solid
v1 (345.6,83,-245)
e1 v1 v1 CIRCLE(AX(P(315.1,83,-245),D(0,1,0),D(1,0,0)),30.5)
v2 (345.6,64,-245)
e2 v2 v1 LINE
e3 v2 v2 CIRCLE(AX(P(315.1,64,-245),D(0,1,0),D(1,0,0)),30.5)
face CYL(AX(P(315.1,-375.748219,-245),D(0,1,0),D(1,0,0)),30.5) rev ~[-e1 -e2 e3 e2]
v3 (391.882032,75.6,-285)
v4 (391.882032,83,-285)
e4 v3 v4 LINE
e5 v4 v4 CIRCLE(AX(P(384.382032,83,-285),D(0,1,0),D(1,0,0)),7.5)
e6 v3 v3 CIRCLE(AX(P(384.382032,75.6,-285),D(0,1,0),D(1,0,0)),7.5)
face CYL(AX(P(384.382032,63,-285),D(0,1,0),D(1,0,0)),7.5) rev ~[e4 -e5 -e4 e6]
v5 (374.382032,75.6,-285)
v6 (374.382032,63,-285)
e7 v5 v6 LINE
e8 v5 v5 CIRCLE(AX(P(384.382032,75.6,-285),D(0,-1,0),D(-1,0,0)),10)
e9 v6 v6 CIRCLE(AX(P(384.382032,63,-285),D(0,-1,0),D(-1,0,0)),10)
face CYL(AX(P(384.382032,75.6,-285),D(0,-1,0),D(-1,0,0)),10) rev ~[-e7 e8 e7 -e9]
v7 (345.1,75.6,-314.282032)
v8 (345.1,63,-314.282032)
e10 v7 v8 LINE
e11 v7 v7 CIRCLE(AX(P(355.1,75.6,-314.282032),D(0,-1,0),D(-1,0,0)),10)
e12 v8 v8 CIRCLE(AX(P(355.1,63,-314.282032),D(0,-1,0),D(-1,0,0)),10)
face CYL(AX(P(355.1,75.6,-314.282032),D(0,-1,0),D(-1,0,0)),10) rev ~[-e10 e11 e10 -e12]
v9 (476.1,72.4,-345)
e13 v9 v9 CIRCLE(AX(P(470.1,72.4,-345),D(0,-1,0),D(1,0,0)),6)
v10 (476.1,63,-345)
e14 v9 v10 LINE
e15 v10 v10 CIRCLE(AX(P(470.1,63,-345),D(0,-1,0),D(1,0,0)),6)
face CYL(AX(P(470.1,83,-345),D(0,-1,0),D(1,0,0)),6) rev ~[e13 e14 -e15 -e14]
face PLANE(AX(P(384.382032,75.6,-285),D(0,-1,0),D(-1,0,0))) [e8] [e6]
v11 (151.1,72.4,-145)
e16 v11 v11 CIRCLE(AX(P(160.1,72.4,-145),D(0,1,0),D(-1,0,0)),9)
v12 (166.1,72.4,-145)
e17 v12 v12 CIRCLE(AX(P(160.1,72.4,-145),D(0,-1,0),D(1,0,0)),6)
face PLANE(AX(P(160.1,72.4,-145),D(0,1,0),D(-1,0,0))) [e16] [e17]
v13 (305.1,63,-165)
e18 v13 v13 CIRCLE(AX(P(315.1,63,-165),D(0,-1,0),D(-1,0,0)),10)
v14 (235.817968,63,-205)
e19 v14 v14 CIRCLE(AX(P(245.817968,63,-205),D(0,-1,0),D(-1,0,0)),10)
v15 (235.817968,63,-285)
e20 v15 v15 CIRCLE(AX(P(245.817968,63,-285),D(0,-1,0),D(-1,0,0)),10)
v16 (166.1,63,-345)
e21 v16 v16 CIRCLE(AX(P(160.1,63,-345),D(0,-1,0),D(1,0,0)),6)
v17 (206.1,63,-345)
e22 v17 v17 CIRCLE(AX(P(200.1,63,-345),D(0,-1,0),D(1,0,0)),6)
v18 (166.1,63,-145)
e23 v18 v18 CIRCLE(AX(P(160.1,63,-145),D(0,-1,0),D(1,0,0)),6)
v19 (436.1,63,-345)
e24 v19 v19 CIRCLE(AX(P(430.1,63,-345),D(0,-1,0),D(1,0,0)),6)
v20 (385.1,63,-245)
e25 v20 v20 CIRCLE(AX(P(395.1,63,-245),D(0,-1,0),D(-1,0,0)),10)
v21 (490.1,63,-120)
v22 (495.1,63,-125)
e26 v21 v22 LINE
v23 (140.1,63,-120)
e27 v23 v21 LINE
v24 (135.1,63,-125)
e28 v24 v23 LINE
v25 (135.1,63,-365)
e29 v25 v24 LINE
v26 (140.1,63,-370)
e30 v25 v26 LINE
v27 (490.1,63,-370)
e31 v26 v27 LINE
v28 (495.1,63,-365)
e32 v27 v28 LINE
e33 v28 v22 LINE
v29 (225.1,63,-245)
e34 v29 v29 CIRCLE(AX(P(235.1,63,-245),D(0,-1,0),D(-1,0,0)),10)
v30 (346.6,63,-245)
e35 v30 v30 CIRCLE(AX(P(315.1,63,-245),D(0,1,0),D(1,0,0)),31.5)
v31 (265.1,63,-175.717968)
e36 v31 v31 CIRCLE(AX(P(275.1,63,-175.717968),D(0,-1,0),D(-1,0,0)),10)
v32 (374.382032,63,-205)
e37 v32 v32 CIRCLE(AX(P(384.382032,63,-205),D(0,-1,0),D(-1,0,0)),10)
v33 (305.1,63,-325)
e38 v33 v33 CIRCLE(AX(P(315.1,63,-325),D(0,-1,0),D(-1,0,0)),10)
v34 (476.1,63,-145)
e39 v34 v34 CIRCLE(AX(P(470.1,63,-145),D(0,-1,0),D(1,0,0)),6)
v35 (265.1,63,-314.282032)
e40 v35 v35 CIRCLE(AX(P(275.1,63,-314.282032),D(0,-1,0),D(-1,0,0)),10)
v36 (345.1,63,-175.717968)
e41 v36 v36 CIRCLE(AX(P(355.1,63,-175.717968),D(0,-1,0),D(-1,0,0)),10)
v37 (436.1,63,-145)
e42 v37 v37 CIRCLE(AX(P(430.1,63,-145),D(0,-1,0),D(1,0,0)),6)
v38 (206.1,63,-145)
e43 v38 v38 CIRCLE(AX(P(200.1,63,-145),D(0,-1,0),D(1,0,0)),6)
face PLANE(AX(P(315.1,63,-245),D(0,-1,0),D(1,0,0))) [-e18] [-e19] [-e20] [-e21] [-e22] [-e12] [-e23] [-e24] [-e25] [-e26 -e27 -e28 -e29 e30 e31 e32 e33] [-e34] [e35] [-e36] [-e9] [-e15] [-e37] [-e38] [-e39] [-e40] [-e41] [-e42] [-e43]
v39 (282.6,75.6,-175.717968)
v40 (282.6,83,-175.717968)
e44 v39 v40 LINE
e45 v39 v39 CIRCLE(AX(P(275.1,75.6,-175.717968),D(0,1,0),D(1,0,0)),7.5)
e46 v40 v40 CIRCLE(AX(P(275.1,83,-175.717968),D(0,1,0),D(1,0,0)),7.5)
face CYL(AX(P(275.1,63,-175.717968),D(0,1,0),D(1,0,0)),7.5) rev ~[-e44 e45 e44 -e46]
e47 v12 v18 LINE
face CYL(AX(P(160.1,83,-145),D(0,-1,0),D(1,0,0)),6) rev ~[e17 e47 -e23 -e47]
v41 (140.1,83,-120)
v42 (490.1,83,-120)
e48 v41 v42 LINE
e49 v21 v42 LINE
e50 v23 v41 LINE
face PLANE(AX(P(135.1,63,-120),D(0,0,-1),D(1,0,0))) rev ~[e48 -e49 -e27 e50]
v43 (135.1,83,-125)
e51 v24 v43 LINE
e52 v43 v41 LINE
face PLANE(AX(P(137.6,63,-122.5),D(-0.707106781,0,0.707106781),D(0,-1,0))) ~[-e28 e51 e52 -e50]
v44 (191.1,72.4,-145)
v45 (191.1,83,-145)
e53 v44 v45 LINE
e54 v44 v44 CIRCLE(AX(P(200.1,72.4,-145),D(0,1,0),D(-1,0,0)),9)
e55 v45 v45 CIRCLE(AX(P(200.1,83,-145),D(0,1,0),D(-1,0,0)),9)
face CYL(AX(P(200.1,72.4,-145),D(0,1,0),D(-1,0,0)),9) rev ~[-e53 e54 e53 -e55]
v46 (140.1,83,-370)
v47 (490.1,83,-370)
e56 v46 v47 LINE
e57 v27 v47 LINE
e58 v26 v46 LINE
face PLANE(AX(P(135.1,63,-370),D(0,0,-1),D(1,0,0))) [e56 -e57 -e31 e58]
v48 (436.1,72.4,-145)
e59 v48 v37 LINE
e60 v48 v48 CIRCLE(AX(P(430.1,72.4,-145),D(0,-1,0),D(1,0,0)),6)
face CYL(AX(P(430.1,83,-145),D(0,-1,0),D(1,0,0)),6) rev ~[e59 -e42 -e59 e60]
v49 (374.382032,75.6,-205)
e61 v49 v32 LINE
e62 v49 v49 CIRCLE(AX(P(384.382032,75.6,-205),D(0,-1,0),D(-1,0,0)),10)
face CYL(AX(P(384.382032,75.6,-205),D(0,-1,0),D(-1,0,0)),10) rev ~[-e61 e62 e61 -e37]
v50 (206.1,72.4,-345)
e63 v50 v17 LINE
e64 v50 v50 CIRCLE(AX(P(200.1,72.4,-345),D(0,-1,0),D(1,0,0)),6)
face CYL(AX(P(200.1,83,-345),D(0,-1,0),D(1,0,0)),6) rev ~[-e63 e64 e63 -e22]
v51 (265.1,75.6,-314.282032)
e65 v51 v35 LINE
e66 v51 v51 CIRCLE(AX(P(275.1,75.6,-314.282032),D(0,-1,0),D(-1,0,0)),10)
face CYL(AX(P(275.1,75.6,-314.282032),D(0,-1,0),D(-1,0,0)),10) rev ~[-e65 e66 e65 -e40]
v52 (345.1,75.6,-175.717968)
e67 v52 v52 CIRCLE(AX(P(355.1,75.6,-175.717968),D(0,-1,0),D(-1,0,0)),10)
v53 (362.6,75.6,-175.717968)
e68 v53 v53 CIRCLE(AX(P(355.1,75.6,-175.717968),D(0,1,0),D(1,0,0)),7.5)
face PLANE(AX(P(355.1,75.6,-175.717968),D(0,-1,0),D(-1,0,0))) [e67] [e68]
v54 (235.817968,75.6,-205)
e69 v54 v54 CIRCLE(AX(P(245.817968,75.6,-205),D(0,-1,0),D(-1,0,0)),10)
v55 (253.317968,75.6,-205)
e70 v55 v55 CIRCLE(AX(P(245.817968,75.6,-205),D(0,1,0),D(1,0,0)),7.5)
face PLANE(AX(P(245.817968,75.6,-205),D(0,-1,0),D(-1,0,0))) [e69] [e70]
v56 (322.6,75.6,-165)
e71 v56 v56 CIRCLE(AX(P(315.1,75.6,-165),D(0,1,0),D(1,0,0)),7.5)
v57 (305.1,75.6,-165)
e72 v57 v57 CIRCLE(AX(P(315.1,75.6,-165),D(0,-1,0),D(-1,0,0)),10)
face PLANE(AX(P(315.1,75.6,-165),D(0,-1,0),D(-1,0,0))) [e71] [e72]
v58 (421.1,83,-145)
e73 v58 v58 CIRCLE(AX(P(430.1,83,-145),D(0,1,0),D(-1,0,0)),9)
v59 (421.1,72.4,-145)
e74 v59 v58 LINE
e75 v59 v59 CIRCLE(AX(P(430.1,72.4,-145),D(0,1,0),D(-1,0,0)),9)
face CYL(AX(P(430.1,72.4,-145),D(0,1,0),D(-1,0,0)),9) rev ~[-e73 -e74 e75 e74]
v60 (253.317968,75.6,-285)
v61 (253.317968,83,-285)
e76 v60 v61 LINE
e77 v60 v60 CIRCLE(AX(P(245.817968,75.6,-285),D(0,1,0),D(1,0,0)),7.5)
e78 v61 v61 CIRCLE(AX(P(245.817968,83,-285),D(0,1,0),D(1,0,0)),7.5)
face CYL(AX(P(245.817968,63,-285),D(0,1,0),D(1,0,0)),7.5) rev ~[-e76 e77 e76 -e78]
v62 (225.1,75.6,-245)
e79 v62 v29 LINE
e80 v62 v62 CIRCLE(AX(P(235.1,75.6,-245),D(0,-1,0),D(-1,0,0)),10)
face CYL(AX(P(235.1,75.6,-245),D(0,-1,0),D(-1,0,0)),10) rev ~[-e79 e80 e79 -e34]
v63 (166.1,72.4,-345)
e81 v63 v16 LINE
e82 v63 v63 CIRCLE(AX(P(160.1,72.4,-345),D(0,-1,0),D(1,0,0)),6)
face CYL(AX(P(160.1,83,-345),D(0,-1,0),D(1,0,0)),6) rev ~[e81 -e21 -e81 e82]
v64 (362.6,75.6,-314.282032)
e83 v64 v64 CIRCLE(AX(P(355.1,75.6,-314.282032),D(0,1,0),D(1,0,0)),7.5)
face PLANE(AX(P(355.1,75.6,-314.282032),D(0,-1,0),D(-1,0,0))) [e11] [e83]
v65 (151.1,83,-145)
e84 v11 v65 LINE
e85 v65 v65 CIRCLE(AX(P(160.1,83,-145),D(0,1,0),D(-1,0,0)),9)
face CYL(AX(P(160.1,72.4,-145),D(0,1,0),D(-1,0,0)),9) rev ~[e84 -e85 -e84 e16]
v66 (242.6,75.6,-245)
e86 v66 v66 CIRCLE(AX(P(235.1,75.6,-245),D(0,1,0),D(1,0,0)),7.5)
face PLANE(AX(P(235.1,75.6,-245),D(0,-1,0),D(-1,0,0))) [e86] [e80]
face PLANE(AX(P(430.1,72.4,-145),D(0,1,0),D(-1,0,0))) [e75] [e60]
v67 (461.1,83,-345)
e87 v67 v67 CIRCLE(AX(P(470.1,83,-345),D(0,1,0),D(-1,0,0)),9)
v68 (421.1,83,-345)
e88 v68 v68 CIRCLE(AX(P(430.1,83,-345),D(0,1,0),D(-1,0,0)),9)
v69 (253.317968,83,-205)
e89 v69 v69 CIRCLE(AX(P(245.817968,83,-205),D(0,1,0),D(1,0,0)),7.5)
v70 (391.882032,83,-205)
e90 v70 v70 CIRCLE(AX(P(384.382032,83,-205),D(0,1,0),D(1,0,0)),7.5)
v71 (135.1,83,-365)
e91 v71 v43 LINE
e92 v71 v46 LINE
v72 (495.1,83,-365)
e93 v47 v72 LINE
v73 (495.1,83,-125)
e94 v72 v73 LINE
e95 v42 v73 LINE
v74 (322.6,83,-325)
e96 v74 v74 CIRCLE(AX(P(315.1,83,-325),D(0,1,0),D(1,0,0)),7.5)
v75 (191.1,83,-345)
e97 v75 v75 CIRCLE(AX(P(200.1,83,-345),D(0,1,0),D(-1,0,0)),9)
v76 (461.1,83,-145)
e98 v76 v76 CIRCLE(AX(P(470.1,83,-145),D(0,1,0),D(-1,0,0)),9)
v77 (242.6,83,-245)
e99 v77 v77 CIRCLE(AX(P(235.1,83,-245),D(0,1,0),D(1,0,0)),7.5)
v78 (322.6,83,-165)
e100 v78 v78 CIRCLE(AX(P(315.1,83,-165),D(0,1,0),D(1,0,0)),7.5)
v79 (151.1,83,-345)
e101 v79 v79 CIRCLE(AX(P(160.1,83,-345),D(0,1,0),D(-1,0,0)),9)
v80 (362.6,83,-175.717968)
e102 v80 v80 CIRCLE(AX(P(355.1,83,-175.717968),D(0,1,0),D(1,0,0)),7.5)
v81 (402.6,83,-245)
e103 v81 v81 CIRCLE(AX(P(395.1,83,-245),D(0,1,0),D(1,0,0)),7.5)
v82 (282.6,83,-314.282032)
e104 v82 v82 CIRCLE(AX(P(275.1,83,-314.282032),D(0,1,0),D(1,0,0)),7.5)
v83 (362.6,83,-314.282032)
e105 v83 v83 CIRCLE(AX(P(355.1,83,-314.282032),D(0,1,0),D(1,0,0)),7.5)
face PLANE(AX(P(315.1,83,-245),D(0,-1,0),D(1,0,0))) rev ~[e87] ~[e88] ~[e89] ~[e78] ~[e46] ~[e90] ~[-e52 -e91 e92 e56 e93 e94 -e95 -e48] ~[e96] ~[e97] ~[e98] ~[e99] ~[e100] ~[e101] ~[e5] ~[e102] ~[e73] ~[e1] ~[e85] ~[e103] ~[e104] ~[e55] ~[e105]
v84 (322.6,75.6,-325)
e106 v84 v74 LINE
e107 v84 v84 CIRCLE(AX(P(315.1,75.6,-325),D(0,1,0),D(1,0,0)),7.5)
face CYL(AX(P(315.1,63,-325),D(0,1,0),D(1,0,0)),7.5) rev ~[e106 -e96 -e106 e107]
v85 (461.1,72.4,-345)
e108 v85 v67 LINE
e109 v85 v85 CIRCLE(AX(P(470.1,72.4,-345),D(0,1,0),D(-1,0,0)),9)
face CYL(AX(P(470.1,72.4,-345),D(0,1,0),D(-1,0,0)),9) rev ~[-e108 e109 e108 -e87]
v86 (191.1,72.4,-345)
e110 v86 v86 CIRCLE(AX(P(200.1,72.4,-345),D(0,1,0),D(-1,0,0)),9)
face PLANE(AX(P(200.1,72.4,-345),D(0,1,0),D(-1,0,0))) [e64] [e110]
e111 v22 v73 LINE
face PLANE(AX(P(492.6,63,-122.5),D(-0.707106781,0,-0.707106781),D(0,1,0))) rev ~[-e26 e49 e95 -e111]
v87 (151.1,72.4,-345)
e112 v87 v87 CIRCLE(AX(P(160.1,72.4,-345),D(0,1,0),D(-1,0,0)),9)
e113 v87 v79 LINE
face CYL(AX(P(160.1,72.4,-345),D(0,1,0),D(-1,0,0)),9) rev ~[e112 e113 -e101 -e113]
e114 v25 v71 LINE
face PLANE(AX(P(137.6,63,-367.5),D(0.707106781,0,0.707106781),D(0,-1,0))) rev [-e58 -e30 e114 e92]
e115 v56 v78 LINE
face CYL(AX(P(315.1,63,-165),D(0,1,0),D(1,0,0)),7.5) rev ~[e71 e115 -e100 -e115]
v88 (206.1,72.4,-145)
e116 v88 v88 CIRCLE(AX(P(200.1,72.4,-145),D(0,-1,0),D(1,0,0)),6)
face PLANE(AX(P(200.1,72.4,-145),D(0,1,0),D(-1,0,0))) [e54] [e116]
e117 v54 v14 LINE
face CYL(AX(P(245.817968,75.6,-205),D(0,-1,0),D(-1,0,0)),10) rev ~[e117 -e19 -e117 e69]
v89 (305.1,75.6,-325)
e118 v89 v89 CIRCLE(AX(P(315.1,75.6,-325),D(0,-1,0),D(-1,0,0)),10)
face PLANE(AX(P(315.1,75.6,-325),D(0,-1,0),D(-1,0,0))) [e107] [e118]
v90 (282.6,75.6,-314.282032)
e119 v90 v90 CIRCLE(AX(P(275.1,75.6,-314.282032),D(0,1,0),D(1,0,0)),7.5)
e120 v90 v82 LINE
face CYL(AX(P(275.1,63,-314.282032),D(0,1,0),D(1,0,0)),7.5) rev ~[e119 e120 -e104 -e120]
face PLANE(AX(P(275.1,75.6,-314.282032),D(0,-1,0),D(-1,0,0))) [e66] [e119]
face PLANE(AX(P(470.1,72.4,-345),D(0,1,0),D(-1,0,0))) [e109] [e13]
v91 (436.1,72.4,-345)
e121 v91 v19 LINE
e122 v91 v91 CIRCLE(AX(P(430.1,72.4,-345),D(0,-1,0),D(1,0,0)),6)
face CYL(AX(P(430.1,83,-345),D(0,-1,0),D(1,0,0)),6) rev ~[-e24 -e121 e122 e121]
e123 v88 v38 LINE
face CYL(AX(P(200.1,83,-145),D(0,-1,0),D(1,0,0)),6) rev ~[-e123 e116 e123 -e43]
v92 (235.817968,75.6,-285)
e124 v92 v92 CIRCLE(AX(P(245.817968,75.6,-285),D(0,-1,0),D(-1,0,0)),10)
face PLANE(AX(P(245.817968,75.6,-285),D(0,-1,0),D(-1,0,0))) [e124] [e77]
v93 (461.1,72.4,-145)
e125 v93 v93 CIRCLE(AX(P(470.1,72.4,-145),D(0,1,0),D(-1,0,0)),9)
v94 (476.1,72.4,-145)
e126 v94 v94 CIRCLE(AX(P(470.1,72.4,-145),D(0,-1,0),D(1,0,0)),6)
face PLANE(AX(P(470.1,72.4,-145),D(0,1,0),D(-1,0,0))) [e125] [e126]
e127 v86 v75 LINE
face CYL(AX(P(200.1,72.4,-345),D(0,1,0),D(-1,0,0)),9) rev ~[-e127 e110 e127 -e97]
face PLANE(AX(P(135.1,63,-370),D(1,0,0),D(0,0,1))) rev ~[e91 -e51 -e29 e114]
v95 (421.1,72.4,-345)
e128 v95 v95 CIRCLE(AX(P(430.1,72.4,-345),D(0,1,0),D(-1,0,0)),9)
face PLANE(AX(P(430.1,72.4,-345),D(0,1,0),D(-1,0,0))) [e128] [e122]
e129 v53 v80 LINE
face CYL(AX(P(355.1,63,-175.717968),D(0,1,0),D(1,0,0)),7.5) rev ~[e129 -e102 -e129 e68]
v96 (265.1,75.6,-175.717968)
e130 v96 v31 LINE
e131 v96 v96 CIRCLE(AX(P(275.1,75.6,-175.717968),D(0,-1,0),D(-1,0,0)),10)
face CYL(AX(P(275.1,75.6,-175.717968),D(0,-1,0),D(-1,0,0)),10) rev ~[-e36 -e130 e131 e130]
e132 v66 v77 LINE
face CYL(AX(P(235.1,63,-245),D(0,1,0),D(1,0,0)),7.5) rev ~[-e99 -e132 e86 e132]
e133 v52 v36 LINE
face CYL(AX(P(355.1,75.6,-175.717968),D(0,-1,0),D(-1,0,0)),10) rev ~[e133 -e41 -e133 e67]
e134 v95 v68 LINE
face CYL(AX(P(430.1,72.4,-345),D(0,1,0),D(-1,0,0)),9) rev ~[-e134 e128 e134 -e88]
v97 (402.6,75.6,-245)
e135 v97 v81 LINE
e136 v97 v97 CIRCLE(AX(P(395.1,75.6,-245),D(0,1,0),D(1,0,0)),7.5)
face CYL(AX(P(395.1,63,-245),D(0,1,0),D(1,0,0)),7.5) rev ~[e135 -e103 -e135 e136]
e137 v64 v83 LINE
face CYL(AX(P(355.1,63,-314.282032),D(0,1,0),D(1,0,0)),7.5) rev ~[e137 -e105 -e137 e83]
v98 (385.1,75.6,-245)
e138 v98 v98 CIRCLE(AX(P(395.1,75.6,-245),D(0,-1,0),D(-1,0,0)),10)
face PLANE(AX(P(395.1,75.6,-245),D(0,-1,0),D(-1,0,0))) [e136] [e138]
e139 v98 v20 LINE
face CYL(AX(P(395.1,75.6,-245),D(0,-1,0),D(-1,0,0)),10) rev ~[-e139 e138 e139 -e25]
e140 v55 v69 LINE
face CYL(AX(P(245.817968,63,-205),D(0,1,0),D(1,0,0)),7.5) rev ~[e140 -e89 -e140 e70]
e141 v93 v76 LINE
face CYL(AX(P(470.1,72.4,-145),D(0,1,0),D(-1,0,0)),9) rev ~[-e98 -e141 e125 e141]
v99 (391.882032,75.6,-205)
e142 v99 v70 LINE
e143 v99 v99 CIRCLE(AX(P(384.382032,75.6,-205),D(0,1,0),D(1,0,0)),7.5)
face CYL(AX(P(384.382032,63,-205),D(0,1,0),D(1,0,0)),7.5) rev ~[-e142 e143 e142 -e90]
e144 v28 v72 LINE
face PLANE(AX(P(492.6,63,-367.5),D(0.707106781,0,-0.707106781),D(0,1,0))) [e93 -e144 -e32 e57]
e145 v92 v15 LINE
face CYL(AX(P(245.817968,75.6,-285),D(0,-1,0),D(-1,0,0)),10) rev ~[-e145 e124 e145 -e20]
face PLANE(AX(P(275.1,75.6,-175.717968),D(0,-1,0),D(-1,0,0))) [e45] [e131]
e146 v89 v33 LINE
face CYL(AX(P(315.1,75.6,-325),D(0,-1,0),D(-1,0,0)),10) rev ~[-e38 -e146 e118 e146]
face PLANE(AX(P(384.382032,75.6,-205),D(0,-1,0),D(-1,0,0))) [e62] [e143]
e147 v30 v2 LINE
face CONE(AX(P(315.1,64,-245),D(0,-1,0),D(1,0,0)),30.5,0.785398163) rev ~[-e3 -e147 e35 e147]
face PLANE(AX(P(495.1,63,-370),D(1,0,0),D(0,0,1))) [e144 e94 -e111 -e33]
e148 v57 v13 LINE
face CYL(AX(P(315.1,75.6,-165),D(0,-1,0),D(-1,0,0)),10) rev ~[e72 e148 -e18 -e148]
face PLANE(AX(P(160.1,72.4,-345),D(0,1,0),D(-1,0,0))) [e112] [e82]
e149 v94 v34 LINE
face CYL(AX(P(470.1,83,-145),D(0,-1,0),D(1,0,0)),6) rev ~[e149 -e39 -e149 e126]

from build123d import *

# Parameters (mm, degrees)
SKETCH_1_W                    = 360
SKETCH_1_H                    = 250
EXTRUDE_1_DEPTH               = 20
HOLE_WIZARD_M10_1_D           = 12
HOLE_WIZARD_M10_1_CBORE_D     = 18
HOLE_WIZARD_M10_1_CBORE_DEPTH = 10.6
HOLE_WIZARD_M52_1_D           = 61
HOLE_WIZARD_M12_1_D           = 15
HOLE_WIZARD_M12_1_CBORE_D     = 20
HOLE_WIZARD_M12_1_CBORE_DEPTH = 12.6
CHAMFER_1_SIZE                = 1
CHAMFER_2_SIZE                = 5


with BuildPart() as part:
    # 草图1 → 凸台-拉伸1 (new body)
    with BuildSketch(Plane.XZ.offset(-63)):
        with Locations((315.1, -245)):
            Rectangle(SKETCH_1_W, SKETCH_1_H)
    extrude(amount=-EXTRUDE_1_DEPTH)

    # M10 六角凹头螺钉的柱形沉头孔1 (through all)
    with Locations(Plane(origin=(0, 83, 0), x_dir=(-1, 0, 0), z_dir=(0, 1, 0))):
        with Locations((-470.1, -345), (-430.1, -345), (-470.1, -145), (-430.1, -145), (-200.1, -145), (-200.1, -345), (-160.1, -145), (-160.1, -345)):
            CounterBoreHole(HOLE_WIZARD_M10_1_D / 2, HOLE_WIZARD_M10_1_CBORE_D / 2, HOLE_WIZARD_M10_1_CBORE_DEPTH)

    # M52 间隙孔1 (through all)
    with Locations(Plane(origin=(0, 63, 0), x_dir=(-1, 0, 0), z_dir=(0, -1, 0))):
        with Locations((-315.1, 245)):
            Hole(HOLE_WIZARD_M52_1_D / 2)

    # M12 六角凹头螺钉的柱形沉头孔1 (through all)
    with Locations(Plane(origin=(0, 63, 0), x_dir=(-1, 0, 0), z_dir=(0, -1, 0))):
        with Locations((-245.817967697, 205), (-275.1, 175.717967697), (-315.1, 165), (-355.1, 175.717967697), (-384.382032303, 205), (-395.1, 245), (-384.382032303, 285), (-355.1, 314.282032303), (-315.1, 325), (-275.1, 314.282032303), (-245.817967697, 285), (-235.1, 245)):
            CounterBoreHole(HOLE_WIZARD_M12_1_D / 2, HOLE_WIZARD_M12_1_CBORE_D / 2, HOLE_WIZARD_M12_1_CBORE_DEPTH)

    # 倒角1
    chamfer_1_edges = [part.edges().sort_by_distance(p)[0] for p in [
        (284.6, 63, -245),
    ]]
    chamfer(chamfer_1_edges, length=CHAMFER_1_SIZE)

    # 倒角2
    chamfer_2_edges = [part.edges().sort_by_distance(p)[0] for p in [
        (495.1, 73, -120),
        (495.1, 73, -370),
        (135.1, 73, -370),
        (135.1, 73, -120),
    ]]
    chamfer(chamfer_2_edges, length=CHAMFER_2_SIZE)


solid = part.part
